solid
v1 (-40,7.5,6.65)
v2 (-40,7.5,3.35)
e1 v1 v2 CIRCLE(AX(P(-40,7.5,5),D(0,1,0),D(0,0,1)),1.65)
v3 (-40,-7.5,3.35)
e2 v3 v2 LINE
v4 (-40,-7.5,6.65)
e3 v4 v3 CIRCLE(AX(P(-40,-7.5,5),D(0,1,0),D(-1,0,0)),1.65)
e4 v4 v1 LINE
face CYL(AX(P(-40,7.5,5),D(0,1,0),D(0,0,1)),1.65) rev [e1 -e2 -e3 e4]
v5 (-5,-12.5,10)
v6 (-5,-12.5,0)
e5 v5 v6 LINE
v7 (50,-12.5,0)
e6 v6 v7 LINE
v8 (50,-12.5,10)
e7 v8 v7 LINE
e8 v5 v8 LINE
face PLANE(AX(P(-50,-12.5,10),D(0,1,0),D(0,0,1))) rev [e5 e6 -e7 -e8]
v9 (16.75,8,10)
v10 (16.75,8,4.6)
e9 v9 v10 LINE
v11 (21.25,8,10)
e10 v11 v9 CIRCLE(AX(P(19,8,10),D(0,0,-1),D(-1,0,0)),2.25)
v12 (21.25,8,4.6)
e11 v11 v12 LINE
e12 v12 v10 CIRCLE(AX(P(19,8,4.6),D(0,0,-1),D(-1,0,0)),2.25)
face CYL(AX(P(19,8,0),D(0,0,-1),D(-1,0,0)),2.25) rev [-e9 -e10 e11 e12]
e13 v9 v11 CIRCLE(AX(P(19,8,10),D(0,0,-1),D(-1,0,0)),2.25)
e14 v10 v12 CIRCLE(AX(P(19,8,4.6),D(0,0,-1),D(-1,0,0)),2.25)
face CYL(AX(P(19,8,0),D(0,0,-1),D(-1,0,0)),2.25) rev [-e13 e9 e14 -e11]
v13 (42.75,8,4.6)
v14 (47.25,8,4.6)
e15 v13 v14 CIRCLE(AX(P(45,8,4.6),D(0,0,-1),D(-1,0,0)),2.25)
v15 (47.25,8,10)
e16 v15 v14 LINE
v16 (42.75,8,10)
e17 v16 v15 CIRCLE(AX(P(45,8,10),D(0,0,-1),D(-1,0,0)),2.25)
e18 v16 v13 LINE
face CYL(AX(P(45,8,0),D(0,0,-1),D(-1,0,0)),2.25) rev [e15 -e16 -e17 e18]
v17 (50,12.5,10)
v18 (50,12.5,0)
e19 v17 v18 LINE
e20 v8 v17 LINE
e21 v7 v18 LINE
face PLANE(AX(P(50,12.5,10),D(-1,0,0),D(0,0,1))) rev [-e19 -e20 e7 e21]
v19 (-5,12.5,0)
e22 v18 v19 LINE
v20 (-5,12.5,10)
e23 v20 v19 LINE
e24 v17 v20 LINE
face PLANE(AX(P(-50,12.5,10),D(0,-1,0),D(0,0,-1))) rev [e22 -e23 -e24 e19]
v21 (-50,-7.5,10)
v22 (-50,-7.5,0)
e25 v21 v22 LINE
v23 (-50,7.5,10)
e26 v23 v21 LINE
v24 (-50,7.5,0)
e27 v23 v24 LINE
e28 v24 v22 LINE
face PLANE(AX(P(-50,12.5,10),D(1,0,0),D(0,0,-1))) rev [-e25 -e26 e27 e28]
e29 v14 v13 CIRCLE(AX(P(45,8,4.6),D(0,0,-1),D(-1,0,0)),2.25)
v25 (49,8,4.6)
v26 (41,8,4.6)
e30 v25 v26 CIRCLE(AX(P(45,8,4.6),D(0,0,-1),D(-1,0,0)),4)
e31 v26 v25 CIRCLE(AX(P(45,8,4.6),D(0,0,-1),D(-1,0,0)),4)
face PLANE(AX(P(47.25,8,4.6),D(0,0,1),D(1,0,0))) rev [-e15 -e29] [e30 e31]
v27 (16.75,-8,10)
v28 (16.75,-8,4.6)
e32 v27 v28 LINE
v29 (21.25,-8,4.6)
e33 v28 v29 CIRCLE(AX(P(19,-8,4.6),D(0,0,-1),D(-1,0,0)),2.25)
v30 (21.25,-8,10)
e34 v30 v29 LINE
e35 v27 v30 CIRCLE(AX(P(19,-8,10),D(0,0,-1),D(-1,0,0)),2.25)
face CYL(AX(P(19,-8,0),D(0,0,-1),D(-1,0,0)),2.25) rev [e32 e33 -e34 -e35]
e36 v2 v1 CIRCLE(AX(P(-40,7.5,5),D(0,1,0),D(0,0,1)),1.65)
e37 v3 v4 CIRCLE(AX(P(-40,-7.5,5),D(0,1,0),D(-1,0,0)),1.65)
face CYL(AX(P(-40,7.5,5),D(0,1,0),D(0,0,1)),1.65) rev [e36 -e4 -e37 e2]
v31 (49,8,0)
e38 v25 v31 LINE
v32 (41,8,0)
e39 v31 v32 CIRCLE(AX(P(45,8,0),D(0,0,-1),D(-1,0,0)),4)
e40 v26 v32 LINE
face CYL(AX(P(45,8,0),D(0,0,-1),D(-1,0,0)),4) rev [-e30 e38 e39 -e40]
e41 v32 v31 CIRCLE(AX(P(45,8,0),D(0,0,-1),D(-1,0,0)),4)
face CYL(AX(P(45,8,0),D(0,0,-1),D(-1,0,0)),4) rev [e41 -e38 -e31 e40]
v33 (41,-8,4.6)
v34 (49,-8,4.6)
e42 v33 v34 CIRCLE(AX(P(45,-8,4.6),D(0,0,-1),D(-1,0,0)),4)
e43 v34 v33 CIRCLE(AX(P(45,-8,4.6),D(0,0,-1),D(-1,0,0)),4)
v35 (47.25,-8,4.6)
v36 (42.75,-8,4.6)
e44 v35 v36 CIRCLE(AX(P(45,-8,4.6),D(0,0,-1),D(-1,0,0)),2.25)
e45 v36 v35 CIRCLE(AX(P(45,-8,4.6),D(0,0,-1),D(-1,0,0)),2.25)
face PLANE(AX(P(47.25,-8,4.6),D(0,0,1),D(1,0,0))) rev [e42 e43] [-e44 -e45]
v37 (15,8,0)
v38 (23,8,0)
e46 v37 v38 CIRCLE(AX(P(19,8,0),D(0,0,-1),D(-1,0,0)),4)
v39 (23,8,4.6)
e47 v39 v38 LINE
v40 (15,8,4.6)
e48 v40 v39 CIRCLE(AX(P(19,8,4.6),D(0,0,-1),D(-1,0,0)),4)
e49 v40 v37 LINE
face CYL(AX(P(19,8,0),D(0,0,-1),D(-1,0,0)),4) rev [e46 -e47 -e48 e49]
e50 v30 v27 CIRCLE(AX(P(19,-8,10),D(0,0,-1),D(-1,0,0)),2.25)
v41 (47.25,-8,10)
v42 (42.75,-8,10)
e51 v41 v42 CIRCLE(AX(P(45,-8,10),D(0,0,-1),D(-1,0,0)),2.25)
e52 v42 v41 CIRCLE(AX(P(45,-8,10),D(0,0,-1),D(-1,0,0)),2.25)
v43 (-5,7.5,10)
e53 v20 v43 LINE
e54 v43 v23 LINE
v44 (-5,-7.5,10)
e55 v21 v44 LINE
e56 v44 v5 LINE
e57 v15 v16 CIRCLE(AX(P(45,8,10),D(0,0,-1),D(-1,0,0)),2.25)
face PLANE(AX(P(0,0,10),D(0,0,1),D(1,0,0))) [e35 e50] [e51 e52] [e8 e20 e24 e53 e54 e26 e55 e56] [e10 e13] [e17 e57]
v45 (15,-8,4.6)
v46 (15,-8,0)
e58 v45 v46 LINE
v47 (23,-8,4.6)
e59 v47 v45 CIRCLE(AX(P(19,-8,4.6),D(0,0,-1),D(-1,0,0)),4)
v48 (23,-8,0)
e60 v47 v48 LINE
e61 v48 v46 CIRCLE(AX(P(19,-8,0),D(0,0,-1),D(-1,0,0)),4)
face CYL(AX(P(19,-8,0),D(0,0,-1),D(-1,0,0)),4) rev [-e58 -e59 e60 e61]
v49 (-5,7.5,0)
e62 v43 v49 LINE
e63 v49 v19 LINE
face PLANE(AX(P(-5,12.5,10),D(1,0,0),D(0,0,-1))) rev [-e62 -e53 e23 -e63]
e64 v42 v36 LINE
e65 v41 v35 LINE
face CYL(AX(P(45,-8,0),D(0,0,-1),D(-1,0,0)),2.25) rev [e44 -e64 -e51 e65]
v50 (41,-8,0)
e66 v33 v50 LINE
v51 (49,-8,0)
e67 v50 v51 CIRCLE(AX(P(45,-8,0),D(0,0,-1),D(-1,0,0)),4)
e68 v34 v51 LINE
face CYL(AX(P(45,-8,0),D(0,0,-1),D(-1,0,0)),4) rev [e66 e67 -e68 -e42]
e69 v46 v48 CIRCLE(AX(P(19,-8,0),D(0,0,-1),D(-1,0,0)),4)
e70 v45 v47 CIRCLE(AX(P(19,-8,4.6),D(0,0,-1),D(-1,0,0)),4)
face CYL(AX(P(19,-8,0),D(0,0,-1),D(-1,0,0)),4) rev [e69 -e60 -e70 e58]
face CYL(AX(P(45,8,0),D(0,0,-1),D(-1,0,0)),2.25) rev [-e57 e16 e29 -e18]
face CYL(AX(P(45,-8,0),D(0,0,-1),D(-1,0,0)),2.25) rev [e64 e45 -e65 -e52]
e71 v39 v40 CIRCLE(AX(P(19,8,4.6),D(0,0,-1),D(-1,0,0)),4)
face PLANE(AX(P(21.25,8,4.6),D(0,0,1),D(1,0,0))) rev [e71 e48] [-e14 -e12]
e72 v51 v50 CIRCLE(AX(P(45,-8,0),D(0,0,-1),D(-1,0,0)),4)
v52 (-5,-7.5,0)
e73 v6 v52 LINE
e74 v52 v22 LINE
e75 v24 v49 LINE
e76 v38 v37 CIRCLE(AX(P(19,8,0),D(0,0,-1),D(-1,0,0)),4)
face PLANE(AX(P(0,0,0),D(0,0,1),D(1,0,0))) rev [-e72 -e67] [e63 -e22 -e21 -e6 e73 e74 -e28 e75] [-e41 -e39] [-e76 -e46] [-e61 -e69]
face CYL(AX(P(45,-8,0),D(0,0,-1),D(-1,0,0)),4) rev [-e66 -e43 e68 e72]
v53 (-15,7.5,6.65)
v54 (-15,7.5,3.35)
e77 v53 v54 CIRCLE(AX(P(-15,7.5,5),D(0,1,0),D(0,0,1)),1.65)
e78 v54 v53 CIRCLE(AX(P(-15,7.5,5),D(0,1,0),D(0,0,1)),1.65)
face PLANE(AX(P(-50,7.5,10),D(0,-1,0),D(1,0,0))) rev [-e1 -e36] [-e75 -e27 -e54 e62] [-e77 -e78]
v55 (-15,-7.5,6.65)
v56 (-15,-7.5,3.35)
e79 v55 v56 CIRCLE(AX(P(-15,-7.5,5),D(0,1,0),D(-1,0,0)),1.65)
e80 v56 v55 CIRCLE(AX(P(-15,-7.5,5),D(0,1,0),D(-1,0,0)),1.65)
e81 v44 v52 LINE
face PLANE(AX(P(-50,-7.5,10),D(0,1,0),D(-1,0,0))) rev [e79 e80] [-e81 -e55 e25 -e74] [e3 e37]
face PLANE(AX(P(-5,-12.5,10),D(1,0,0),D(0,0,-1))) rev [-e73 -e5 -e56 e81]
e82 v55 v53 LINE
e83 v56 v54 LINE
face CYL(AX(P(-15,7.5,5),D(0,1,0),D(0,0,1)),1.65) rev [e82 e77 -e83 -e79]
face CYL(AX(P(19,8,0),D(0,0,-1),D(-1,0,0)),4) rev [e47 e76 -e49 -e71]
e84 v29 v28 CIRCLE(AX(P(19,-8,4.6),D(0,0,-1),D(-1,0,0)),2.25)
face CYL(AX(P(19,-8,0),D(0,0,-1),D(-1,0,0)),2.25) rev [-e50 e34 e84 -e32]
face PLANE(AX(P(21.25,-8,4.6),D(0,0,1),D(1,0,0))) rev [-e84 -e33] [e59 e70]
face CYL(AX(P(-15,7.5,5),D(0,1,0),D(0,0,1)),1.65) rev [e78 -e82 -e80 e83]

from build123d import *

# Parameters (mm, degrees)
SKETCH1_W                                        = 100
SKETCH1_H                                        = 25
BOSS_EXTRUDE1_DEPTH                              = 10
CUT_EXTRUDE1_DEPTH                               = 53.5
CUT_EXTRUDE1_DEPTH_BACK                          = 53.5
SKETCH2_W                                        = 45
SKETCH2_H                                        = 5
HOLE_FOR_SOCKET_HEAD_CAP_SCREW_TYPE1_D           = 4.5
HOLE_FOR_SOCKET_HEAD_CAP_SCREW_TYPE1_CBORE_D     = 8
HOLE_FOR_SOCKET_HEAD_CAP_SCREW_TYPE1_CBORE_DEPTH = 4.6
M4_TAPPED_HOLE1_D                                = 3.3


with BuildPart() as part:
    # Sketch1 → Boss-Extrude1 (new body)
    with BuildSketch(Plane.XY):
        Rectangle(SKETCH1_W, SKETCH1_H)
    extrude(amount=BOSS_EXTRUDE1_DEPTH)

    # Sketch2 → Cut-Extrude1 (cut, two sides: drawn at the far end of the back side and taken through both)
    with BuildSketch(Plane(origin=(0, 0, 0), x_dir=(-1, 0, 0), z_dir=(0, 0, -1)).offset(-CUT_EXTRUDE1_DEPTH_BACK)):
        with Locations((27.5, 10)):
            Rectangle(SKETCH2_W, SKETCH2_H)
        with Locations((27.5, -10)):
            Rectangle(SKETCH2_W, SKETCH2_H)
    extrude(amount=CUT_EXTRUDE1_DEPTH + CUT_EXTRUDE1_DEPTH_BACK, mode=Mode.SUBTRACT)

    # Hole for socket head cap screw, type1 (through all)
    with Locations(Plane(origin=(0, 0, 0), x_dir=(-1, 0, 0), z_dir=(0, 0, -1))):
        with Locations((-19, -8), (-19, 8), (-45, 8), (-45, -8)):
            CounterBoreHole(HOLE_FOR_SOCKET_HEAD_CAP_SCREW_TYPE1_D / 2, HOLE_FOR_SOCKET_HEAD_CAP_SCREW_TYPE1_CBORE_D / 2, HOLE_FOR_SOCKET_HEAD_CAP_SCREW_TYPE1_CBORE_DEPTH)

    # M4 Tapped Hole1 (through all)
    with Locations(Plane(origin=(0, 7.5, 0), x_dir=(1, 0, 0), z_dir=(0, 1, 0))):
        with Locations((-15, -5), (-40, -5)):
            Hole(M4_TAPPED_HOLE1_D / 2)


solid = part.part
